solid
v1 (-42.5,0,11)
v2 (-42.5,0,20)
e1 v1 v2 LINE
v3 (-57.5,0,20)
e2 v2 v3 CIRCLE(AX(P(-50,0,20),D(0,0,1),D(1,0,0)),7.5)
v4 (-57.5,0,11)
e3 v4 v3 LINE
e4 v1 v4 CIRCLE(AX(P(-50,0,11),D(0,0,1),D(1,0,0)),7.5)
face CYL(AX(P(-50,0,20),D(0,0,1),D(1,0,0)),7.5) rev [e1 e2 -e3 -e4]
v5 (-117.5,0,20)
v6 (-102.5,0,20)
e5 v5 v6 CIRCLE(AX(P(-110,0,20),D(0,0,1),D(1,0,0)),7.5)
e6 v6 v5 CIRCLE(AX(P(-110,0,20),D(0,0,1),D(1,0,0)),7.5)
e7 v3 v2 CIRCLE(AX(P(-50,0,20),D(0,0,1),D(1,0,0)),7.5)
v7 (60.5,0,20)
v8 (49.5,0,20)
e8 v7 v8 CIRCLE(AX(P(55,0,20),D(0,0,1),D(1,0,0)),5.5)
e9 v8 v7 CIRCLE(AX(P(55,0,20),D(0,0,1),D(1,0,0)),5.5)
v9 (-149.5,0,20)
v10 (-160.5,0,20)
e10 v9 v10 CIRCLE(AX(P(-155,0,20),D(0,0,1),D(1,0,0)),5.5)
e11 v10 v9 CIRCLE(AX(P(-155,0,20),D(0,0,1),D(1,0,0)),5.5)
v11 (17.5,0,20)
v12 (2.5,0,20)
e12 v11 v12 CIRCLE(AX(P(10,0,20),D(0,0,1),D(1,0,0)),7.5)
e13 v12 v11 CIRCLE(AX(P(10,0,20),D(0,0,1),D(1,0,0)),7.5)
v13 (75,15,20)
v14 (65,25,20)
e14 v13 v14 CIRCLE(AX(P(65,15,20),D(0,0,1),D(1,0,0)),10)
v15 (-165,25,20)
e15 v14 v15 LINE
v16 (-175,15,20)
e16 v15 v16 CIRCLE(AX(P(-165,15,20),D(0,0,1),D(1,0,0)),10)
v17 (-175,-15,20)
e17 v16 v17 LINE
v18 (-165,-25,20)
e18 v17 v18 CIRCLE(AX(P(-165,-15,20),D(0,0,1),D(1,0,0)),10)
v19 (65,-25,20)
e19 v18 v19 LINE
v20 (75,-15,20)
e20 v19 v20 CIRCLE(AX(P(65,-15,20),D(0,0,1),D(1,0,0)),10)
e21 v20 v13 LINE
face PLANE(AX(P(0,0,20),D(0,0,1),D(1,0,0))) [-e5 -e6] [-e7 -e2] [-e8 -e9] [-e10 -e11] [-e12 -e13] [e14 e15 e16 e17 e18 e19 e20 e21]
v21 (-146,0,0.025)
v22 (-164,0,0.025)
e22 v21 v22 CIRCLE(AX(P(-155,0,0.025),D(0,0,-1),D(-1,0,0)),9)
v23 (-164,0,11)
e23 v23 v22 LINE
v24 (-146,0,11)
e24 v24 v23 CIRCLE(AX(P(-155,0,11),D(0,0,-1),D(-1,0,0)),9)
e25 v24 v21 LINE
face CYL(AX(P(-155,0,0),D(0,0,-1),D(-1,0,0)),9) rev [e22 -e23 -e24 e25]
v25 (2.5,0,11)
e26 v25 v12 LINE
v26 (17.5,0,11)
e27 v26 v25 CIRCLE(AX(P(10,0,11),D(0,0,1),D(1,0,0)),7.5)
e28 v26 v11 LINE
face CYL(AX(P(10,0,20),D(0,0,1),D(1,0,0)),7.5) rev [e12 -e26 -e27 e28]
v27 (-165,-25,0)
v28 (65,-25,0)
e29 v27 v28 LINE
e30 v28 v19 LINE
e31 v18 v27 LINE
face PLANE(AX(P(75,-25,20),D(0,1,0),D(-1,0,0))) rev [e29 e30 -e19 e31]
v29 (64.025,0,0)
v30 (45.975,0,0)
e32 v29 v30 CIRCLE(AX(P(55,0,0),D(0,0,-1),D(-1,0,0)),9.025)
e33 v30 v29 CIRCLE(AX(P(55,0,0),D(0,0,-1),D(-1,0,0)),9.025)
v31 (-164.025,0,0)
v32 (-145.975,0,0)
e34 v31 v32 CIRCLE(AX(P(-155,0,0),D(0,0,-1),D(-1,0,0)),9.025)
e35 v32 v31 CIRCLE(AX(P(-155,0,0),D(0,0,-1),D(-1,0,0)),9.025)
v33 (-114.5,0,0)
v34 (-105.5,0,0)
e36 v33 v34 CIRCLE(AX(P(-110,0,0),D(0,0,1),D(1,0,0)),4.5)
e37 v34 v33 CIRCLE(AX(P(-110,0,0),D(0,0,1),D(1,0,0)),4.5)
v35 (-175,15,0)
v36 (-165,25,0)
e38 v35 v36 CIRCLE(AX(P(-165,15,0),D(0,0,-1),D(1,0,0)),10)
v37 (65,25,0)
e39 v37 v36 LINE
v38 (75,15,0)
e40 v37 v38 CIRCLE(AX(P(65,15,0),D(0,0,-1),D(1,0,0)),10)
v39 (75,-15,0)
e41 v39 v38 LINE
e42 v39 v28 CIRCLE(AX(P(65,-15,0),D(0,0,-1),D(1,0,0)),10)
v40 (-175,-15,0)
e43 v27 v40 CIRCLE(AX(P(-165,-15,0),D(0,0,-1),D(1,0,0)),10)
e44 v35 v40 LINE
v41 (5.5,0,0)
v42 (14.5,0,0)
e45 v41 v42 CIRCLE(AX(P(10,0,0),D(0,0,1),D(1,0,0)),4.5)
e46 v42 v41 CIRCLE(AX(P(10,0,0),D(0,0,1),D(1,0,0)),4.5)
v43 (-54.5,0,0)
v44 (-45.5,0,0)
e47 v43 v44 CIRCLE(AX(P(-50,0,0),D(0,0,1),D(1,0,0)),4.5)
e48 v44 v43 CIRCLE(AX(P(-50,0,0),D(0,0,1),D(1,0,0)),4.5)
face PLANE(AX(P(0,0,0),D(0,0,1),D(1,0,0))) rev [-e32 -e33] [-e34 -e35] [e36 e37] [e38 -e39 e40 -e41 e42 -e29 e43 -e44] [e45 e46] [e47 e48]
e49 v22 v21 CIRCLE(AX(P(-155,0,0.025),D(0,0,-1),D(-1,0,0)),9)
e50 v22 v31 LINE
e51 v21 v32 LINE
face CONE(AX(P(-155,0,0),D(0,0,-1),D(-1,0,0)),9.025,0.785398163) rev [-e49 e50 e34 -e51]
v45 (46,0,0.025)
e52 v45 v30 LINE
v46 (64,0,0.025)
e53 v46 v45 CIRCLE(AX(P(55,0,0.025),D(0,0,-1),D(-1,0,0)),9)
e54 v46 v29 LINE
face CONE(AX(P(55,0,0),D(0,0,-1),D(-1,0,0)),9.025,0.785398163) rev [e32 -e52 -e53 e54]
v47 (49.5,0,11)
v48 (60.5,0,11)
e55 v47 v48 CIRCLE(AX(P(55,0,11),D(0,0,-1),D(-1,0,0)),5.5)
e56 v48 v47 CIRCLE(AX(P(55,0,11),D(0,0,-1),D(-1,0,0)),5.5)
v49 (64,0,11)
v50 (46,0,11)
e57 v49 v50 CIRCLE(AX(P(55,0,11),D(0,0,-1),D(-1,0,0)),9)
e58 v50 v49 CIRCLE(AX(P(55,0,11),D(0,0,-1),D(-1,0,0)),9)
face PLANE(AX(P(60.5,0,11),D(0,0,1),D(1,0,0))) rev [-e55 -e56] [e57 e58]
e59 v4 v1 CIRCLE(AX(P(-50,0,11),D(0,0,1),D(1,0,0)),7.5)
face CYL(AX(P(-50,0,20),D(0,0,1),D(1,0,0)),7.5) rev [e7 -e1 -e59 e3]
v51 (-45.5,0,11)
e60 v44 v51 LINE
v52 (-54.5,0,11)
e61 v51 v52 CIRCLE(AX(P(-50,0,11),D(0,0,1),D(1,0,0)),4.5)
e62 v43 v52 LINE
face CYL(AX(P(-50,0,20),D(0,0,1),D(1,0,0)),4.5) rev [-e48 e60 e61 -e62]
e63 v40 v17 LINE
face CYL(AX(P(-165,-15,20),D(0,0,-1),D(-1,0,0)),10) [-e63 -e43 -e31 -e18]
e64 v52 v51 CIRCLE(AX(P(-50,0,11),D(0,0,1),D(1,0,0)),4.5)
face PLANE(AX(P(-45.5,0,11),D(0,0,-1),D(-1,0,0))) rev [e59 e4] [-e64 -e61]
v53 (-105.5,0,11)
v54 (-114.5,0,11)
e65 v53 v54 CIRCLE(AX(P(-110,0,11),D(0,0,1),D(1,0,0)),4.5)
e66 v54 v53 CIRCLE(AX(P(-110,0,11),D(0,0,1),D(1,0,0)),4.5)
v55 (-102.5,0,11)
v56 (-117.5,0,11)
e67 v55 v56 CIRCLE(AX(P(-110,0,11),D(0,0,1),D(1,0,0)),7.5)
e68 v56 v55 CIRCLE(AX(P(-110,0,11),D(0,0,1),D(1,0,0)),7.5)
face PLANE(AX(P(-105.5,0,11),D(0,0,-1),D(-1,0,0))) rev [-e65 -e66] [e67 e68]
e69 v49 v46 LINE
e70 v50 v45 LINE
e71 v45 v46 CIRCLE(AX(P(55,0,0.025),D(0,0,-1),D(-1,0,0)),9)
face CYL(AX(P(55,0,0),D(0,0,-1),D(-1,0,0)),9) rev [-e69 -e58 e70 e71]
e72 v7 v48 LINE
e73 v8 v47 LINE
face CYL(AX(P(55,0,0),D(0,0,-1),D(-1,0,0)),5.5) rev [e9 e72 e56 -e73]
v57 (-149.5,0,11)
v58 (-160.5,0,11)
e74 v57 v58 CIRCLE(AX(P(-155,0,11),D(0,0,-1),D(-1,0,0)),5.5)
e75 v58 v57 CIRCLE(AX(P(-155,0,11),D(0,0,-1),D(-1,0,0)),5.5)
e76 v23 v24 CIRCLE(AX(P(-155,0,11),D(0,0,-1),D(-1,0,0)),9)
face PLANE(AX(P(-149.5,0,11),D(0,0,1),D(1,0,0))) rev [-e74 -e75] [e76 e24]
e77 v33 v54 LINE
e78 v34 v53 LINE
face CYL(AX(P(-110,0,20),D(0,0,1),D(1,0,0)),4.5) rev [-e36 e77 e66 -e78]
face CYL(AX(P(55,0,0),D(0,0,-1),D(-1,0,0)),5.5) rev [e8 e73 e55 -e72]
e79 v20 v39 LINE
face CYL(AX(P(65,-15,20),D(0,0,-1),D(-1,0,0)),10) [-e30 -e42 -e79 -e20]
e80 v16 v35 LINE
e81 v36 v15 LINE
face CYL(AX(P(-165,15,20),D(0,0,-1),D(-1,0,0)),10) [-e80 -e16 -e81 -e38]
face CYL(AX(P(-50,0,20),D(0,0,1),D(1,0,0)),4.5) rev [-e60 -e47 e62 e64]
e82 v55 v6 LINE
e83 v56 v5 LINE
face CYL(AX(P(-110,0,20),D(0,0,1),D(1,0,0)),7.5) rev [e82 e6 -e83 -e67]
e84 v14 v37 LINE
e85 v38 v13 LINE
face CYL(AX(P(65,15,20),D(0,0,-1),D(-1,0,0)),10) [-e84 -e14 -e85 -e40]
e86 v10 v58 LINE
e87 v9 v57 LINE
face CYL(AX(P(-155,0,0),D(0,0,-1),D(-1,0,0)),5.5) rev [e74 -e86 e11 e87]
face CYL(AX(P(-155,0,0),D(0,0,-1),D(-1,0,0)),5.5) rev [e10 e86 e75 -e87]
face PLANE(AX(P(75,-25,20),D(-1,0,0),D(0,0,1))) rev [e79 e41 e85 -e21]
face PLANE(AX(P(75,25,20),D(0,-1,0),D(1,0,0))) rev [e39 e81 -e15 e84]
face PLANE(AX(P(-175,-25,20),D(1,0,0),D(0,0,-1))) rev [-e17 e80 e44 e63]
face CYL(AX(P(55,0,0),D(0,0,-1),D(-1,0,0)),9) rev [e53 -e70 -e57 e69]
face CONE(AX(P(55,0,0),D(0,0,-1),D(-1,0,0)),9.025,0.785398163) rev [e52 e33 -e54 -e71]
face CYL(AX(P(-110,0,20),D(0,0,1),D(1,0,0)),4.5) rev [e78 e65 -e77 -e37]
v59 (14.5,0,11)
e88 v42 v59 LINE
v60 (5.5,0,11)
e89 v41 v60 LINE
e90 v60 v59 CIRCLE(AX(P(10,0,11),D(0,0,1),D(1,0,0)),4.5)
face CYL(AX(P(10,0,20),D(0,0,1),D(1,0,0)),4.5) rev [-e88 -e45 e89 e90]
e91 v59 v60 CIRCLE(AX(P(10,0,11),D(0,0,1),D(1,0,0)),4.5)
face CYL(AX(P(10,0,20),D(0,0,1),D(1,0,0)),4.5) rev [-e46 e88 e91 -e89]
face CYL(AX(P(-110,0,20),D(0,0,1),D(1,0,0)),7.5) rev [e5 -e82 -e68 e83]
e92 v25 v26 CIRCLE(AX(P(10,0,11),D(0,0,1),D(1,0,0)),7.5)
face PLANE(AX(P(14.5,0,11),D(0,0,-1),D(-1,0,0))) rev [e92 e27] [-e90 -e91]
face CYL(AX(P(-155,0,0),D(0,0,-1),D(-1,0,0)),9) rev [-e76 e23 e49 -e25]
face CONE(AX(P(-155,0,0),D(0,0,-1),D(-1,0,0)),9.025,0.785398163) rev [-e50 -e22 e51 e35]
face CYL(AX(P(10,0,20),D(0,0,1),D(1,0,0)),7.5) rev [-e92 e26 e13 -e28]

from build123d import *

# Parameters (mm, degrees)
SKETCH1_W                                    = 250
SKETCH1_H                                    = 50
BOSS_EXTRUDE1_DEPTH                          = 20
FILLET1_R                                    = 10
LPATTERN1_COUNT                              = 3
LPATTERN1_PITCH                              = 60
CBORE_FOR_M10_HEXAGON_SOCKET_HEAD_CA_2_COUNT = 2
CBORE_FOR_M10_HEXAGON_SOCKET_HEAD_CA_2_PITCH = 210


with BuildPart() as part:
    # Sketch1 → Boss-Extrude1 (new body)
    with BuildSketch(Plane.XY):
        with Locations((-50, 0)):
            Rectangle(SKETCH1_W, SKETCH1_H)
    extrude(amount=BOSS_EXTRUDE1_DEPTH)

    # Fillet1
    fillet1_edges = [part.edges().sort_by_distance(p)[0] for p in [
        (-175, 25, 10),
        (75, 25, 10),
        (75, -25, 10),
        (-175, -25, 10),
    ]]
    fillet(fillet1_edges, radius=FILLET1_R)

    # Sketch2 → CBORE for M8 Hexagon socket head cap screws1 (revolve, cut)
    with BuildSketch(Plane(origin=(10, 0, 20), x_dir=(0, -1, 0), z_dir=(1, 0, 0))):
        Polygon((0, 0), (0, 24.953872786), (4.5, 22.25), (4.5, 9), (7.5, 9), (7.5, 0), align=None)
    cbore_for_m8_hexagon_socket_head_cap_scr = revolve(axis=Axis((10, 0, 26.35), (0, 0, -1)), mode=Mode.SUBTRACT)

    # LPattern1: CBORE for M8 Hexagon socket head cap screws1 ×3
    with Locations(*[(-i * LPATTERN1_PITCH, 0, 0) for i in range(1, LPATTERN1_COUNT)]):
        add(cbore_for_m8_hexagon_socket_head_cap_scr, mode=Mode.SUBTRACT)

    # Sketch4 → CBORE for M10 Hexagon socket head cap screws1 (revolve, cut)
    with BuildSketch(Plane.YZ.offset(55)):
        Polygon((0, 0), (0, 30.804733405), (5.5, 27.5), (5.5, 11), (9, 11), (9, 0.025), (9.025, 0), align=None)
    cbore_for_m10_hexagon_socket_head_cap_sc = revolve(axis=Axis((55, 0, -6.35), (0, 0, 1)), mode=Mode.SUBTRACT)

    # CBORE for M10 Hexagon socket head ca 2: CBORE for M10 Hexagon socket head cap screws1 ×2
    with Locations(*[(-i * CBORE_FOR_M10_HEXAGON_SOCKET_HEAD_CA_2_PITCH, 0, 0) for i in range(1, CBORE_FOR_M10_HEXAGON_SOCKET_HEAD_CA_2_COUNT)]):
        add(cbore_for_m10_hexagon_socket_head_cap_sc, mode=Mode.SUBTRACT)


solid = part.part
